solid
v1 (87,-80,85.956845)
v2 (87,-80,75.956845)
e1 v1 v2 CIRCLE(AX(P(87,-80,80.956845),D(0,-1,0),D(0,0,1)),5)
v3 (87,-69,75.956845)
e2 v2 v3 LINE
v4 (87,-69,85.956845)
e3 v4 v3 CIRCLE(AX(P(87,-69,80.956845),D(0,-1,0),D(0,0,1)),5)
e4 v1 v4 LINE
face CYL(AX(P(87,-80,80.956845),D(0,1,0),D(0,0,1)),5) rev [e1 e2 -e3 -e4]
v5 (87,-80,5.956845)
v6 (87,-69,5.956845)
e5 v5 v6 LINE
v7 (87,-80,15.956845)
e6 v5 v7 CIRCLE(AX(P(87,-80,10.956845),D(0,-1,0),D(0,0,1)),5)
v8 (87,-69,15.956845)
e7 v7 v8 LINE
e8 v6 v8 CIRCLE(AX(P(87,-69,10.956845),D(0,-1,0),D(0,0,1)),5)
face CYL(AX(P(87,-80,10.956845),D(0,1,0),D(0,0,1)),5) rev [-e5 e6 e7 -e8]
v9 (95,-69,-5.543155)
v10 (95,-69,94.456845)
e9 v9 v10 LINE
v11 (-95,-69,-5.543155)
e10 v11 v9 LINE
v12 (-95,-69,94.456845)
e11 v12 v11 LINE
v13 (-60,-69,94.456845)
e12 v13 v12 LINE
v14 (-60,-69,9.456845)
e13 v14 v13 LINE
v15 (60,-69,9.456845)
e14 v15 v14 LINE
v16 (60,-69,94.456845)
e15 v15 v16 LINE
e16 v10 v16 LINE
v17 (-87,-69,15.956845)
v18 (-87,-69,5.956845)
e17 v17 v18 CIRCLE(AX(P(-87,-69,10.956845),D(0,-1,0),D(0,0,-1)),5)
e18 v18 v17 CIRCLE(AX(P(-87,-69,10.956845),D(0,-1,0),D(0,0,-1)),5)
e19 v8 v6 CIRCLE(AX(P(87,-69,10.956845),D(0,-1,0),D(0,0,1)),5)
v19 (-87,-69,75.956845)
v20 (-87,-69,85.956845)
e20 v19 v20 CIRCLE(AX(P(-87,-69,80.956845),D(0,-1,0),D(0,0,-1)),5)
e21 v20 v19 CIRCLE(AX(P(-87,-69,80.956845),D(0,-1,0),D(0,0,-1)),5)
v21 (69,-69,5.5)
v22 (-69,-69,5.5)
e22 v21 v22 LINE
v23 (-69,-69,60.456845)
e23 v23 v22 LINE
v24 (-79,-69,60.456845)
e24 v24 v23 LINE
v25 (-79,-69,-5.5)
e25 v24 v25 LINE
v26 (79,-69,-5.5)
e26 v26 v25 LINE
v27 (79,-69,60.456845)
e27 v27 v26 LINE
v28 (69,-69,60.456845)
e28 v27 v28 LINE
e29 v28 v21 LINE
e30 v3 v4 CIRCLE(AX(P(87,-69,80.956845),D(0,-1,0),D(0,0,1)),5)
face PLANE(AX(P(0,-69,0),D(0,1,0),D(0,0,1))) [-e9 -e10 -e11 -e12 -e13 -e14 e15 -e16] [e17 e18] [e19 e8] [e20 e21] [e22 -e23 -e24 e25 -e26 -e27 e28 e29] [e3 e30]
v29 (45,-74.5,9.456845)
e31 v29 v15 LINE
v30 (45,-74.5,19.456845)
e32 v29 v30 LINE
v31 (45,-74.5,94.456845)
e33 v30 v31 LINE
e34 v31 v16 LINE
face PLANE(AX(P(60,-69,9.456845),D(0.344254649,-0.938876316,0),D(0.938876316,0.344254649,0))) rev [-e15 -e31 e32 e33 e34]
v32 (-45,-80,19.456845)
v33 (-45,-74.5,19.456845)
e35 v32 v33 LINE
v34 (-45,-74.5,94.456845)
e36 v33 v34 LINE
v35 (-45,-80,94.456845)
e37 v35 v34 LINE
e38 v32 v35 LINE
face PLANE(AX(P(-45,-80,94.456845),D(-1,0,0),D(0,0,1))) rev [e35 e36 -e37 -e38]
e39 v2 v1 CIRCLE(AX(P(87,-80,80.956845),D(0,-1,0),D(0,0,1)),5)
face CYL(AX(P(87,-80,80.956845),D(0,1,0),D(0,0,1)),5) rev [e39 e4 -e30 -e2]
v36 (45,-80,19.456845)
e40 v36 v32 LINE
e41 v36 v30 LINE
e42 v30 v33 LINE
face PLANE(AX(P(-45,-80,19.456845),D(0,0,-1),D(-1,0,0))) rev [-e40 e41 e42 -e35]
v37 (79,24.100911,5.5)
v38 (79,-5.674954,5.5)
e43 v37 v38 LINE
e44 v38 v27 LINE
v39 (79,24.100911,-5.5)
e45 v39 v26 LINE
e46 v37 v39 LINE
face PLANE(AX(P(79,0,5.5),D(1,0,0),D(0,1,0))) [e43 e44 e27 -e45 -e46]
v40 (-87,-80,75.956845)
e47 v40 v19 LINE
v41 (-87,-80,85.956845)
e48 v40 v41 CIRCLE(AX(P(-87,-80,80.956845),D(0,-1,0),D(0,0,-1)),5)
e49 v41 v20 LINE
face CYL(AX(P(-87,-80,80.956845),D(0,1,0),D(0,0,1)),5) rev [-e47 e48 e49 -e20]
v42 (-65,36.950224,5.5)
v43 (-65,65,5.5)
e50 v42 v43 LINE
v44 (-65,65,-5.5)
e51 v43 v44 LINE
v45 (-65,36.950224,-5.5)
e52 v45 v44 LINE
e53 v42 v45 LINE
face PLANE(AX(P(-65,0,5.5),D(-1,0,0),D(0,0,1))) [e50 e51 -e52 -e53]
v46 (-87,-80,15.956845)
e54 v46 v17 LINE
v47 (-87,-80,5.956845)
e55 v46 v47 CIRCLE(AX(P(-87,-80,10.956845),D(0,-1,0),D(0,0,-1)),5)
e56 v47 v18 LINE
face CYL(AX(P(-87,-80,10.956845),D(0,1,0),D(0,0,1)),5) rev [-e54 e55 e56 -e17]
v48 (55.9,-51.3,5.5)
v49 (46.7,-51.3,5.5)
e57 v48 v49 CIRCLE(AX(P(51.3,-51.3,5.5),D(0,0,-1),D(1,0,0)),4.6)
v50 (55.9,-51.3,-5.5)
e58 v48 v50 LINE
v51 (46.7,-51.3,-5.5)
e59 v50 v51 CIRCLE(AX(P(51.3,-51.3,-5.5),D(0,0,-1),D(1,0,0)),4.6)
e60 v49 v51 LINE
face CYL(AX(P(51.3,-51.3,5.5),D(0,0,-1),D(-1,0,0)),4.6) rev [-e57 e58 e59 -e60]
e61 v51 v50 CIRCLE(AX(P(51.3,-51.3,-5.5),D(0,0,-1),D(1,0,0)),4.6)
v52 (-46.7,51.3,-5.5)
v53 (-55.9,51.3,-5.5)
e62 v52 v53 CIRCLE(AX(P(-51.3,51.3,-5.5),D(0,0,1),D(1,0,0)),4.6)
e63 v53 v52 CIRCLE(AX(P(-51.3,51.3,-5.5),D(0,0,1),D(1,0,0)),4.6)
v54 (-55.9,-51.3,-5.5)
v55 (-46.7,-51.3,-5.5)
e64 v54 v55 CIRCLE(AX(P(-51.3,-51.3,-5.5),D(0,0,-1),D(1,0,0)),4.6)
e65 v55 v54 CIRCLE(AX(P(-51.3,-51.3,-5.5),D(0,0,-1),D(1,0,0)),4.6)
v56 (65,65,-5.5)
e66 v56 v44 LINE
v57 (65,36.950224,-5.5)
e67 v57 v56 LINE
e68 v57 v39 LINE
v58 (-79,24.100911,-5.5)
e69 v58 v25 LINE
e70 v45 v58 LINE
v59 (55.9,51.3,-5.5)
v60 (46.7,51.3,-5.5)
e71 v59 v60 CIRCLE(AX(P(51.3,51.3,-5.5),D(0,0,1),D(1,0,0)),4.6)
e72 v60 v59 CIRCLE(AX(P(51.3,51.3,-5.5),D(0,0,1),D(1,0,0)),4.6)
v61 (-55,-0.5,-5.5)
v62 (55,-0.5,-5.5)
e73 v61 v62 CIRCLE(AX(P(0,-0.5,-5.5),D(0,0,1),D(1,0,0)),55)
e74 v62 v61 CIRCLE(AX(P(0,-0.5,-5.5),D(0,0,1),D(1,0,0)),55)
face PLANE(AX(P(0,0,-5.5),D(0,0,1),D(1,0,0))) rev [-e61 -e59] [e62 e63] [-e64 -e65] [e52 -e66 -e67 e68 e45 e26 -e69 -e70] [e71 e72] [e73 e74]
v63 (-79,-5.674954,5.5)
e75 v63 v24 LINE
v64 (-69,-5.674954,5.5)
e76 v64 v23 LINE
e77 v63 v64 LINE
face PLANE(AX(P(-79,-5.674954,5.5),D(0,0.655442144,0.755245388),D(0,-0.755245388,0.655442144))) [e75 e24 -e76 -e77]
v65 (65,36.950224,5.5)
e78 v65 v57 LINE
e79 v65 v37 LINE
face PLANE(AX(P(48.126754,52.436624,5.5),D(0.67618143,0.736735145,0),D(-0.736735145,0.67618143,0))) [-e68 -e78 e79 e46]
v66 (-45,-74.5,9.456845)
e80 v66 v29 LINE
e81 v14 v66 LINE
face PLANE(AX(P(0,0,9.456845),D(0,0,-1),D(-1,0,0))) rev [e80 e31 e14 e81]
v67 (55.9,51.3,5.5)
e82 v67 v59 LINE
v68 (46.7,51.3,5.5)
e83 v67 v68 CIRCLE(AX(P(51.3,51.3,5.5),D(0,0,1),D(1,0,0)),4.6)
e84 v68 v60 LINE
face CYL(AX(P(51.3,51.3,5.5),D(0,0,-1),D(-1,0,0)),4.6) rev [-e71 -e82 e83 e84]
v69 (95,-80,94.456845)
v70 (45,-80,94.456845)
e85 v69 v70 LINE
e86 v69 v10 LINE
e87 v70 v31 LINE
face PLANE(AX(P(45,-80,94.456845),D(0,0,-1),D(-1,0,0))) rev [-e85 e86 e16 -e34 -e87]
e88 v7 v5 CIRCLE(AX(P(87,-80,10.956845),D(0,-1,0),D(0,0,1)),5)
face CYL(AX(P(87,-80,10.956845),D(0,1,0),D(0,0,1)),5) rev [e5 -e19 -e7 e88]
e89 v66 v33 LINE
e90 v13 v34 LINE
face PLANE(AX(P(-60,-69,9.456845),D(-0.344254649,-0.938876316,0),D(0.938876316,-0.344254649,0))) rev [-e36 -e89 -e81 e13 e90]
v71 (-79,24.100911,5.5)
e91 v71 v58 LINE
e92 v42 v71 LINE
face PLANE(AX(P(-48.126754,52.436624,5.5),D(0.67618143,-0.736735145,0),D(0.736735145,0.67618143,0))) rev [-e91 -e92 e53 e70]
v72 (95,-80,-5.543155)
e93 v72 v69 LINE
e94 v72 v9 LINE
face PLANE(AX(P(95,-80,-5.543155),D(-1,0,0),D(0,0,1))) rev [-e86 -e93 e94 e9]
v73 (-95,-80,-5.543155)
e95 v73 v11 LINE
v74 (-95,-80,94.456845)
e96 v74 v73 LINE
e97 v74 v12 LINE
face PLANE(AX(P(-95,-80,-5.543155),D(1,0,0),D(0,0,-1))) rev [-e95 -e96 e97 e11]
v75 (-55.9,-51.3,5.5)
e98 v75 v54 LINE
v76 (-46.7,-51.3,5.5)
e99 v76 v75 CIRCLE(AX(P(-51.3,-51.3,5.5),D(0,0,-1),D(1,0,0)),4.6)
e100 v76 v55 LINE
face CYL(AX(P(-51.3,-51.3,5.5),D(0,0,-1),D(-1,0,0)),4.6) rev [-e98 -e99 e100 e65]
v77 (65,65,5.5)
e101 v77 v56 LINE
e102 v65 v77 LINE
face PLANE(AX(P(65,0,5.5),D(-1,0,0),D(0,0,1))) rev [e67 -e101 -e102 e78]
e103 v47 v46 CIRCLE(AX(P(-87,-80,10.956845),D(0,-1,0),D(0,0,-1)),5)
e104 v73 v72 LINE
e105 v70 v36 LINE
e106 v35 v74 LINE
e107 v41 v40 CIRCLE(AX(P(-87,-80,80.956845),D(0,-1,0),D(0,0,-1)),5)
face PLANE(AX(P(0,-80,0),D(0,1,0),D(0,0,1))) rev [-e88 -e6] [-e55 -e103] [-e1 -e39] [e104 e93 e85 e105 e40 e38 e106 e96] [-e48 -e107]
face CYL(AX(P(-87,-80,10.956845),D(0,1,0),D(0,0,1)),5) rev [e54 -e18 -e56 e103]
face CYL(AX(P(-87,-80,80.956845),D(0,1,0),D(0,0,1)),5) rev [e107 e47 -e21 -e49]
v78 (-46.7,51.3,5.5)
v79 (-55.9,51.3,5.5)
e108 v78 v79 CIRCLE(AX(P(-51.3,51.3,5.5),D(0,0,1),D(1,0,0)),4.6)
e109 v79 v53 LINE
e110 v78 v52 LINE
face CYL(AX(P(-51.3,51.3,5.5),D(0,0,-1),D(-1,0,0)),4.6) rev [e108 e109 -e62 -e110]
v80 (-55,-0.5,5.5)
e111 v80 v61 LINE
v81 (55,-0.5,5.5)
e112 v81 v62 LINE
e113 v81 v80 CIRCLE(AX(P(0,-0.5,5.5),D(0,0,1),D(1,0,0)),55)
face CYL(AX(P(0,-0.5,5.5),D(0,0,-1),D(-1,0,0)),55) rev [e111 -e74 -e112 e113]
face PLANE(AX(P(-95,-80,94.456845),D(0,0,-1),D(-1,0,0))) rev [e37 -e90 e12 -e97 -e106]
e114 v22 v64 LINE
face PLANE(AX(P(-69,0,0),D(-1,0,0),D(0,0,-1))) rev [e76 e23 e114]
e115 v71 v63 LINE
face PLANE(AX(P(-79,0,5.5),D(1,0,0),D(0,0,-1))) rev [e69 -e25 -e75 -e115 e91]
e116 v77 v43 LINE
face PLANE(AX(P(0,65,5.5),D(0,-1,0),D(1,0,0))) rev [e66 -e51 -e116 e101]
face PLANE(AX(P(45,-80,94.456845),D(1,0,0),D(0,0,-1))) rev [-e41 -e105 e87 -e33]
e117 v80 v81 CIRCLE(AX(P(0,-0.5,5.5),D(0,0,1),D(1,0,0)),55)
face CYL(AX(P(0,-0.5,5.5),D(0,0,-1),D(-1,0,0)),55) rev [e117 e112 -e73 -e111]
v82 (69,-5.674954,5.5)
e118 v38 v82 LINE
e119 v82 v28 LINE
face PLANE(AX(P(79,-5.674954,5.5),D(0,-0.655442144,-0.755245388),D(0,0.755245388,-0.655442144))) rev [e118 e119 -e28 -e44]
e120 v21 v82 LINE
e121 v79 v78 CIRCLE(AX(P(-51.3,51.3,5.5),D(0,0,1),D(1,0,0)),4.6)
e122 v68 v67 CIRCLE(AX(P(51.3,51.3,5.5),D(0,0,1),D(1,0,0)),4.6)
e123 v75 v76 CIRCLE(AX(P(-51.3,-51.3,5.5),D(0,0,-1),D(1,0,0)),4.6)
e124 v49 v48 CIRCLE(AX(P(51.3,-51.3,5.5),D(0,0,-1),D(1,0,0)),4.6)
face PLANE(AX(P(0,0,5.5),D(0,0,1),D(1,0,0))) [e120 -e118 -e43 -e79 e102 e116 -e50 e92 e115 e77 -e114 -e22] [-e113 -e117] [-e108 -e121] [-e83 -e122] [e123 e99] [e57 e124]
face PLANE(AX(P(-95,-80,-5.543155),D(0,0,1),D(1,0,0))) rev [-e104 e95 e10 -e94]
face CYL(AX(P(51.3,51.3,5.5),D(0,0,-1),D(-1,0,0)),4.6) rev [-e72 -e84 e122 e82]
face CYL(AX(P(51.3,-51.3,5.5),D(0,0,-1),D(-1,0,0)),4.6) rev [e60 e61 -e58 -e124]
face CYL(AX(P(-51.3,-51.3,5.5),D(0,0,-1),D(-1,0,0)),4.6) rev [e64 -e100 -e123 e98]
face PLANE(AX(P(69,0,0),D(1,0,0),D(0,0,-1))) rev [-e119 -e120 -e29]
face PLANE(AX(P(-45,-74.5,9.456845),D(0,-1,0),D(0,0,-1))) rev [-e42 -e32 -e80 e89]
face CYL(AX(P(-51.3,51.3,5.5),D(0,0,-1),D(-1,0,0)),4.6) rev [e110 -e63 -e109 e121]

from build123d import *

# Parameters (mm, degrees)
SKETCH_1_W          = 130
SKETCH_1_H          = 130
SKETCH_1_R          = 4.6
SKETCH_1_R_2        = 55
SKETCH_1_H_2        = 4
EXTRUDE_1_DEPTH     = 5.5
SKETCH_2_R          = 5
EXTRUDE_2_DEPTH     = 11
EXTRUDE_3_DEPTH     = 5
CUT_EXTRUDE_1_DEPTH = 85


with BuildPart() as part:
    # 草图1 → 凸台-拉伸1 (new, symmetric)
    # profile 1 of 4: a face of its own
    with BuildSketch(Plane.XY):
        Rectangle(SKETCH_1_W, SKETCH_1_H)
        with Locations((51.3, -51.3)):
            Circle(SKETCH_1_R, mode=Mode.SUBTRACT)
        with Locations((51.3, 51.3)):
            Circle(SKETCH_1_R, mode=Mode.SUBTRACT)
        with Locations((-51.3, 51.3)):
            Circle(SKETCH_1_R, mode=Mode.SUBTRACT)
        with Locations((0, -0.5)):
            Circle(SKETCH_1_R_2, mode=Mode.SUBTRACT)
        with Locations((-51.3, -51.3)):
            Circle(SKETCH_1_R, mode=Mode.SUBTRACT)
    # profile 2 of 4: a face of its own
    with BuildSketch(Plane.XY):
        with Locations((0, -67)):
            Rectangle(SKETCH_1_W, SKETCH_1_H_2)
    # profile 3 of 4: a face of its own
    with BuildSketch(Plane.XY):
        Polygon((-65, -69), (-65, -65), (-65, 36.950223859), (-79, 24.100911478), (-79, 0), (-79, -69), align=None)
    # profile 4 of 4: a face of its own
    with BuildSketch(Plane.XY):
        Polygon((79, 0), (79, 24.100911478), (65, 36.950223859), (65, -65), (65, -69), (79, -69), align=None)
    extrude(amount=EXTRUDE_1_DEPTH, both=True)

    # 草图2 → 凸台-拉伸2 (add)
    with BuildSketch(Plane.XZ.offset(69)):
        Polygon((-95, -5.543155134), (95, -5.543155134), (95, 94.456844866), (45, 94.456844866), (45, 19.456844866), (-45, 19.456844866), (-45, 94.456844866), (-95, 94.456844866), align=None)
        with Locations(Location((-87, 80.956844866, 0), (0, 0, 270))):
            Circle(SKETCH_2_R, mode=Mode.SUBTRACT)
        with Locations(Location((-87, 10.956844866, 0), (0, 0, 270))):
            Circle(SKETCH_2_R, mode=Mode.SUBTRACT)
        with Locations(Location((87, 10.956844866, 0), (0, 0, 90))):
            Circle(SKETCH_2_R, mode=Mode.SUBTRACT)
        with Locations(Location((87, 80.956844866, 0), (0, 0, 90))):
            Circle(SKETCH_2_R, mode=Mode.SUBTRACT)
    extrude(amount=EXTRUDE_2_DEPTH)

    # 草图3 → 凸台-拉伸3 (add, symmetric)
    with BuildSketch(Plane(origin=(74, 0, 0), x_dir=(0, 0, -1), z_dir=(1, 0, 0))):
        Polygon((-5.5, -5.674954384), (-60.456844866, -69), (-5.5, -69), align=None)
    extrude_3 = extrude(amount=EXTRUDE_3_DEPTH, both=True)

    # 镜向1: 凸台-拉伸3 across plane
    add(extrude_3.mirror(Plane(origin=(0, 0, 0), x_dir=(0, 0, 1), z_dir=(1, 0, 0))))

    # 草图4 → 切除-拉伸1 (cut)
    with BuildSketch(Plane.XY.offset(94.456844866)):
        Polygon((-60, -69), (-45, -74.5), (45, -74.5), (60, -69), align=None)
    extrude(amount=-CUT_EXTRUDE_1_DEPTH, mode=Mode.SUBTRACT)


solid = part.part
